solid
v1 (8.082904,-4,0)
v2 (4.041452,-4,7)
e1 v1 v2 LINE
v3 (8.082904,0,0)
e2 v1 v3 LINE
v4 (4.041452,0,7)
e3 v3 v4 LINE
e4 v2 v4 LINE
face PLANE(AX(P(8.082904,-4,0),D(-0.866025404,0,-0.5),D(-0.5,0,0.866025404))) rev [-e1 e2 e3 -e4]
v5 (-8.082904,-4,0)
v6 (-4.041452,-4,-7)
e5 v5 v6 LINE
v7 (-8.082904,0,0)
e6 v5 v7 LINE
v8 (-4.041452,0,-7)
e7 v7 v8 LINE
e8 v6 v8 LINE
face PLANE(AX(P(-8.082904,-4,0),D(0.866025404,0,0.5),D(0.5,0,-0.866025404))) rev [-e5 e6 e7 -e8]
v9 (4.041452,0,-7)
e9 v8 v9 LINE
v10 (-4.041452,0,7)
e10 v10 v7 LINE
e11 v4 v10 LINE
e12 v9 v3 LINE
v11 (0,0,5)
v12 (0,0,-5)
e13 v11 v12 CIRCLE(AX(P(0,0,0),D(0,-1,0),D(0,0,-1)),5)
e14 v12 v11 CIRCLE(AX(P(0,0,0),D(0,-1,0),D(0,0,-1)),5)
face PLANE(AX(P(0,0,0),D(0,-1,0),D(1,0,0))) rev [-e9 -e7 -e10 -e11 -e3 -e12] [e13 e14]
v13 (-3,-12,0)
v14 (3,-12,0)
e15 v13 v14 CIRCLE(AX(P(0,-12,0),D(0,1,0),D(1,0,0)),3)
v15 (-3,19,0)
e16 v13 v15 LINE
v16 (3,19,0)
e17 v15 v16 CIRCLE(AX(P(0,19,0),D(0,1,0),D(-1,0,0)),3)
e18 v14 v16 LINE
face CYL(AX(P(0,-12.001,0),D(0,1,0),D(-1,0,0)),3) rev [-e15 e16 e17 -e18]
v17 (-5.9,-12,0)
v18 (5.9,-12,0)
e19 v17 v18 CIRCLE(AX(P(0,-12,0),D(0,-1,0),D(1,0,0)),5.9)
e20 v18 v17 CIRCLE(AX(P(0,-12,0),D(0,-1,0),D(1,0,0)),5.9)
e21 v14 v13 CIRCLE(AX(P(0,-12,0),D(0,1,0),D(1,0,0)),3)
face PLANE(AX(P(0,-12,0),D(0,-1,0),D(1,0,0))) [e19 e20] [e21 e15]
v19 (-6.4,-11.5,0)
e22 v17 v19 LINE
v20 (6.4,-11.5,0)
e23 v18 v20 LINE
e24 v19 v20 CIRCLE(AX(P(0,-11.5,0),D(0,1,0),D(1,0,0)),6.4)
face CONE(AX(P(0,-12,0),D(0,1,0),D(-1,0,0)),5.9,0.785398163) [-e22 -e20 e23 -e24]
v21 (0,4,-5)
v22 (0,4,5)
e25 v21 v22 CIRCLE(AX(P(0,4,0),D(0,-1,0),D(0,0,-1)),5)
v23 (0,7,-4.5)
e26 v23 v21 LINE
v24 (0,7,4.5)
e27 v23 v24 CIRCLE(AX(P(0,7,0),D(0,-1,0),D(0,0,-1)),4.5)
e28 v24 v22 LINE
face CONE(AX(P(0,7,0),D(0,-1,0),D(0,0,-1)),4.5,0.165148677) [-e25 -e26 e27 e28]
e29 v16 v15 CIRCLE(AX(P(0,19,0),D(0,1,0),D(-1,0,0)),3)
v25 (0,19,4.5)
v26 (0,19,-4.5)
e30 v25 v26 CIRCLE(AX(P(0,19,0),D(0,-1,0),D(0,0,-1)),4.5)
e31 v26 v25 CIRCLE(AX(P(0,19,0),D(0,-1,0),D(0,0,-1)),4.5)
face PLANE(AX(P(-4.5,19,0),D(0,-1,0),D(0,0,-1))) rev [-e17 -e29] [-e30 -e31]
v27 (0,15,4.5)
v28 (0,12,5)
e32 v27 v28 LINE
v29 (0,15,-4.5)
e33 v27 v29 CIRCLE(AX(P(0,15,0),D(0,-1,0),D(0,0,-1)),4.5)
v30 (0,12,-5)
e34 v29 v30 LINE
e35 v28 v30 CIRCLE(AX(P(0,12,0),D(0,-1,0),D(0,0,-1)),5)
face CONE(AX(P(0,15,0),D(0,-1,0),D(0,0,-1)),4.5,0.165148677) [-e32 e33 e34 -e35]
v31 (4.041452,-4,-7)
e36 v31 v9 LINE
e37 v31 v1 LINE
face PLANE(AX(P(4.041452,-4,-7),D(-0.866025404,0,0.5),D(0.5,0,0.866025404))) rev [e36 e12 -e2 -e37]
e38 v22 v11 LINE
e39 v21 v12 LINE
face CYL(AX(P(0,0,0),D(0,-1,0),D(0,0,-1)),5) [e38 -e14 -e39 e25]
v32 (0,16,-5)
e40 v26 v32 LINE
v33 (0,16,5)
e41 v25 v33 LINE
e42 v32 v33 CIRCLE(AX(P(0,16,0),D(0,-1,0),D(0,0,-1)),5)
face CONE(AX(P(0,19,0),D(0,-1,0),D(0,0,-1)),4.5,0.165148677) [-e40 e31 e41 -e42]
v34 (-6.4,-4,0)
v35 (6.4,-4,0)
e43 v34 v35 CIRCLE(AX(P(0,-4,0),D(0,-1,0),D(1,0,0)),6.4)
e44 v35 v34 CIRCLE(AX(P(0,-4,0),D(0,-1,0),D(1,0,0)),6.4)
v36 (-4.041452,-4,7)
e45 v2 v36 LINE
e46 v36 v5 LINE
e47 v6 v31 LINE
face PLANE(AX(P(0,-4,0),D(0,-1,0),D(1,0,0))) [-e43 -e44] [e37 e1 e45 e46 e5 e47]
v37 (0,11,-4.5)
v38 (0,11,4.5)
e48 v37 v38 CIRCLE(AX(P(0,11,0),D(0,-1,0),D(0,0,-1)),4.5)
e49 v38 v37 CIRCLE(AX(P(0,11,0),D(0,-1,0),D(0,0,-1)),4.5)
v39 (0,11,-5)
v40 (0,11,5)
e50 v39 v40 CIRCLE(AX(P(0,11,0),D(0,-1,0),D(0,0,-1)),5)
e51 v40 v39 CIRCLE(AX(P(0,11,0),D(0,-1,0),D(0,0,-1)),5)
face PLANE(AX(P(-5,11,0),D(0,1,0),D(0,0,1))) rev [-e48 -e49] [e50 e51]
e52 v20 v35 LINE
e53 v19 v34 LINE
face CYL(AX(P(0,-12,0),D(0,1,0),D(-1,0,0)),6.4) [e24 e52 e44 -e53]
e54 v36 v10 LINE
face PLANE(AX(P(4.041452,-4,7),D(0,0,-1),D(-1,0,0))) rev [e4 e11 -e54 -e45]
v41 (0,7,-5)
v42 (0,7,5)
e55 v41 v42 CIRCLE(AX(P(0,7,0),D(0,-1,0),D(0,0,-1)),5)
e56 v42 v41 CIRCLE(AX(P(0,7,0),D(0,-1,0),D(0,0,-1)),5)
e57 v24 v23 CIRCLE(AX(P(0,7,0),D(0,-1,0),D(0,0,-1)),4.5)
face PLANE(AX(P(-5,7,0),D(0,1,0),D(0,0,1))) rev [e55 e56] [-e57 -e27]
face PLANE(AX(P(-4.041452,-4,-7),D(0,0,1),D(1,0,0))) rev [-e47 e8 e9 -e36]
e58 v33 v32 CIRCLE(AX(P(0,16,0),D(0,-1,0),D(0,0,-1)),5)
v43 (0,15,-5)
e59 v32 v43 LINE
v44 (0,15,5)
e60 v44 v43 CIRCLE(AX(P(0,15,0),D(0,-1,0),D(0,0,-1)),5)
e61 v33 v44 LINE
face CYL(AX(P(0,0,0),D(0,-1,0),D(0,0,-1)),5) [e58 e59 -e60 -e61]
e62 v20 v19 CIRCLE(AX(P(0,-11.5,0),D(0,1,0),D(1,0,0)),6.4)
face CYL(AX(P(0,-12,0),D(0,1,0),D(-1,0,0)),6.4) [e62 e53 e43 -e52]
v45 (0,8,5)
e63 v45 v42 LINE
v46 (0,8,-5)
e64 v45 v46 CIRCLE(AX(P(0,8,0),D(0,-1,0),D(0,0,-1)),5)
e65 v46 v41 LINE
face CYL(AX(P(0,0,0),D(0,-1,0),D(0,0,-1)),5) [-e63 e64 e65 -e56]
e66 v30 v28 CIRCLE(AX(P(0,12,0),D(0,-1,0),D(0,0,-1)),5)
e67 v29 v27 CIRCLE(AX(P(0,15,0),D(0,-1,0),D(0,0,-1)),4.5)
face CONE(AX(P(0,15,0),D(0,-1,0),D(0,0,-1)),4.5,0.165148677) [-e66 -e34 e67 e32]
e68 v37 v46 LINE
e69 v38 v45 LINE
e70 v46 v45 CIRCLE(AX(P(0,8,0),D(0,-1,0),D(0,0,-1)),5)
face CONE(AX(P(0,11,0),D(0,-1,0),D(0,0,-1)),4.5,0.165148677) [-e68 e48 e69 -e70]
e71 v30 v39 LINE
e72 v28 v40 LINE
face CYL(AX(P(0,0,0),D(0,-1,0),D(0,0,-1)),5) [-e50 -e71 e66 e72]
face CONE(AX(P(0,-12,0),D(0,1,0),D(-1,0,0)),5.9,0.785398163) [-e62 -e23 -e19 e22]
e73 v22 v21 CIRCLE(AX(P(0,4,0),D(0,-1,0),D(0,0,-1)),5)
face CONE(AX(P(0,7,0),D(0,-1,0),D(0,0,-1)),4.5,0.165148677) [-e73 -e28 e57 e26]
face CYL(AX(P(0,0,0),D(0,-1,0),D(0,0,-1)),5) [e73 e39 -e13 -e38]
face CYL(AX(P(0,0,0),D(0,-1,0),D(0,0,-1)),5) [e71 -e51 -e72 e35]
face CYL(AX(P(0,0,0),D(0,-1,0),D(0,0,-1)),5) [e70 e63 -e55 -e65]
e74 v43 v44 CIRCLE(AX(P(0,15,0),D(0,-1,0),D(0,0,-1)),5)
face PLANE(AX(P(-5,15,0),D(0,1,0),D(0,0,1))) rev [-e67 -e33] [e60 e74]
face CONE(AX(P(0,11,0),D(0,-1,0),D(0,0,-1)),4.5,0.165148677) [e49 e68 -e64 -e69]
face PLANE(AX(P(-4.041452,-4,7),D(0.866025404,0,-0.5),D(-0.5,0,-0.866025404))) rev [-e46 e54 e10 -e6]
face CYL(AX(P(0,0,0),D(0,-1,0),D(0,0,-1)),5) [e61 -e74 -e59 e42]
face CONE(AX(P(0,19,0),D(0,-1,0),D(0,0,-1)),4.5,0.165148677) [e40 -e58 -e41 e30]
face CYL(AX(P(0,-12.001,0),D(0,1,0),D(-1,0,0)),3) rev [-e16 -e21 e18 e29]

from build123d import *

# Parameters (mm, degrees)
EXTRUDE_1_DEPTH     = 4
SKETCH_3_R          = 6.4
EXTRUDE_2_DEPTH     = 8
CUT_EXTRUDE_1_REACH = 34.792
SKETCH_4_R          = 3
CHAMFER_1_SIZE      = 0.5


with BuildPart() as part:
    # 草图1 → 旋转1 (revolve)
    with BuildSketch(Plane.XY, mode=Mode.PRIVATE) as revolve_1_sk:
        Polygon((-5, 4), (-4.5, 7), (-5, 7), (-5, 8), (-4.5, 11), (-5, 11), (-5, 12), (-4.5, 15), (-5, 15), (-5, 16), (-4.5, 19), (0, 19), (0, 0), (-5, 0), align=None)
    revolve(revolve_1_sk.sketch.rotate(Axis((0, 0, 0), (0, 1, 0)), 270), axis=Axis((0, 0, 0), (0, 1, 0)))

    # 草图2 → 凸台-拉伸1 (add)
    with BuildSketch(Plane.XZ):
        Polygon((8.082903769, 0), (4.041451884, 7), (-4.041451884, 7), (-8.082903769, 0), (-4.041451884, -7), (4.041451884, -7), align=None)
    extrude(amount=EXTRUDE_1_DEPTH)

    # 草图3 → 凸台-拉伸2 (add)
    with BuildSketch(Plane.XZ.offset(4)):
        Circle(SKETCH_3_R)
    extrude(amount=EXTRUDE_2_DEPTH)

    # 草图4 → 切除-拉伸1 (cut, up to next)
    with BuildSketch(Plane(origin=(0, 19, 0), x_dir=(1, 0, 0), z_dir=(0, 1, 0)), mode=Mode.PRIVATE) as cut_extrude_1_sk1:
        with Locations(Location((0, 0, 0), (0, 0, 180))):
            Circle(SKETCH_4_R)
    cut_extrude_1_tool1 = extrude(cut_extrude_1_sk1.sketch, amount=-CUT_EXTRUDE_1_REACH, mode=Mode.PRIVATE) & part.part
    add(cut_extrude_1_tool1.solids().sort_by_distance((0, 19, 0))[0], mode=Mode.SUBTRACT)

    # 倒角1
    chamfer_1_edges = [part.edges().sort_by_distance(p)[0] for p in [
        (-6.4, -12, 0),
    ]]
    chamfer(chamfer_1_edges, length=CHAMFER_1_SIZE)


solid = part.part
